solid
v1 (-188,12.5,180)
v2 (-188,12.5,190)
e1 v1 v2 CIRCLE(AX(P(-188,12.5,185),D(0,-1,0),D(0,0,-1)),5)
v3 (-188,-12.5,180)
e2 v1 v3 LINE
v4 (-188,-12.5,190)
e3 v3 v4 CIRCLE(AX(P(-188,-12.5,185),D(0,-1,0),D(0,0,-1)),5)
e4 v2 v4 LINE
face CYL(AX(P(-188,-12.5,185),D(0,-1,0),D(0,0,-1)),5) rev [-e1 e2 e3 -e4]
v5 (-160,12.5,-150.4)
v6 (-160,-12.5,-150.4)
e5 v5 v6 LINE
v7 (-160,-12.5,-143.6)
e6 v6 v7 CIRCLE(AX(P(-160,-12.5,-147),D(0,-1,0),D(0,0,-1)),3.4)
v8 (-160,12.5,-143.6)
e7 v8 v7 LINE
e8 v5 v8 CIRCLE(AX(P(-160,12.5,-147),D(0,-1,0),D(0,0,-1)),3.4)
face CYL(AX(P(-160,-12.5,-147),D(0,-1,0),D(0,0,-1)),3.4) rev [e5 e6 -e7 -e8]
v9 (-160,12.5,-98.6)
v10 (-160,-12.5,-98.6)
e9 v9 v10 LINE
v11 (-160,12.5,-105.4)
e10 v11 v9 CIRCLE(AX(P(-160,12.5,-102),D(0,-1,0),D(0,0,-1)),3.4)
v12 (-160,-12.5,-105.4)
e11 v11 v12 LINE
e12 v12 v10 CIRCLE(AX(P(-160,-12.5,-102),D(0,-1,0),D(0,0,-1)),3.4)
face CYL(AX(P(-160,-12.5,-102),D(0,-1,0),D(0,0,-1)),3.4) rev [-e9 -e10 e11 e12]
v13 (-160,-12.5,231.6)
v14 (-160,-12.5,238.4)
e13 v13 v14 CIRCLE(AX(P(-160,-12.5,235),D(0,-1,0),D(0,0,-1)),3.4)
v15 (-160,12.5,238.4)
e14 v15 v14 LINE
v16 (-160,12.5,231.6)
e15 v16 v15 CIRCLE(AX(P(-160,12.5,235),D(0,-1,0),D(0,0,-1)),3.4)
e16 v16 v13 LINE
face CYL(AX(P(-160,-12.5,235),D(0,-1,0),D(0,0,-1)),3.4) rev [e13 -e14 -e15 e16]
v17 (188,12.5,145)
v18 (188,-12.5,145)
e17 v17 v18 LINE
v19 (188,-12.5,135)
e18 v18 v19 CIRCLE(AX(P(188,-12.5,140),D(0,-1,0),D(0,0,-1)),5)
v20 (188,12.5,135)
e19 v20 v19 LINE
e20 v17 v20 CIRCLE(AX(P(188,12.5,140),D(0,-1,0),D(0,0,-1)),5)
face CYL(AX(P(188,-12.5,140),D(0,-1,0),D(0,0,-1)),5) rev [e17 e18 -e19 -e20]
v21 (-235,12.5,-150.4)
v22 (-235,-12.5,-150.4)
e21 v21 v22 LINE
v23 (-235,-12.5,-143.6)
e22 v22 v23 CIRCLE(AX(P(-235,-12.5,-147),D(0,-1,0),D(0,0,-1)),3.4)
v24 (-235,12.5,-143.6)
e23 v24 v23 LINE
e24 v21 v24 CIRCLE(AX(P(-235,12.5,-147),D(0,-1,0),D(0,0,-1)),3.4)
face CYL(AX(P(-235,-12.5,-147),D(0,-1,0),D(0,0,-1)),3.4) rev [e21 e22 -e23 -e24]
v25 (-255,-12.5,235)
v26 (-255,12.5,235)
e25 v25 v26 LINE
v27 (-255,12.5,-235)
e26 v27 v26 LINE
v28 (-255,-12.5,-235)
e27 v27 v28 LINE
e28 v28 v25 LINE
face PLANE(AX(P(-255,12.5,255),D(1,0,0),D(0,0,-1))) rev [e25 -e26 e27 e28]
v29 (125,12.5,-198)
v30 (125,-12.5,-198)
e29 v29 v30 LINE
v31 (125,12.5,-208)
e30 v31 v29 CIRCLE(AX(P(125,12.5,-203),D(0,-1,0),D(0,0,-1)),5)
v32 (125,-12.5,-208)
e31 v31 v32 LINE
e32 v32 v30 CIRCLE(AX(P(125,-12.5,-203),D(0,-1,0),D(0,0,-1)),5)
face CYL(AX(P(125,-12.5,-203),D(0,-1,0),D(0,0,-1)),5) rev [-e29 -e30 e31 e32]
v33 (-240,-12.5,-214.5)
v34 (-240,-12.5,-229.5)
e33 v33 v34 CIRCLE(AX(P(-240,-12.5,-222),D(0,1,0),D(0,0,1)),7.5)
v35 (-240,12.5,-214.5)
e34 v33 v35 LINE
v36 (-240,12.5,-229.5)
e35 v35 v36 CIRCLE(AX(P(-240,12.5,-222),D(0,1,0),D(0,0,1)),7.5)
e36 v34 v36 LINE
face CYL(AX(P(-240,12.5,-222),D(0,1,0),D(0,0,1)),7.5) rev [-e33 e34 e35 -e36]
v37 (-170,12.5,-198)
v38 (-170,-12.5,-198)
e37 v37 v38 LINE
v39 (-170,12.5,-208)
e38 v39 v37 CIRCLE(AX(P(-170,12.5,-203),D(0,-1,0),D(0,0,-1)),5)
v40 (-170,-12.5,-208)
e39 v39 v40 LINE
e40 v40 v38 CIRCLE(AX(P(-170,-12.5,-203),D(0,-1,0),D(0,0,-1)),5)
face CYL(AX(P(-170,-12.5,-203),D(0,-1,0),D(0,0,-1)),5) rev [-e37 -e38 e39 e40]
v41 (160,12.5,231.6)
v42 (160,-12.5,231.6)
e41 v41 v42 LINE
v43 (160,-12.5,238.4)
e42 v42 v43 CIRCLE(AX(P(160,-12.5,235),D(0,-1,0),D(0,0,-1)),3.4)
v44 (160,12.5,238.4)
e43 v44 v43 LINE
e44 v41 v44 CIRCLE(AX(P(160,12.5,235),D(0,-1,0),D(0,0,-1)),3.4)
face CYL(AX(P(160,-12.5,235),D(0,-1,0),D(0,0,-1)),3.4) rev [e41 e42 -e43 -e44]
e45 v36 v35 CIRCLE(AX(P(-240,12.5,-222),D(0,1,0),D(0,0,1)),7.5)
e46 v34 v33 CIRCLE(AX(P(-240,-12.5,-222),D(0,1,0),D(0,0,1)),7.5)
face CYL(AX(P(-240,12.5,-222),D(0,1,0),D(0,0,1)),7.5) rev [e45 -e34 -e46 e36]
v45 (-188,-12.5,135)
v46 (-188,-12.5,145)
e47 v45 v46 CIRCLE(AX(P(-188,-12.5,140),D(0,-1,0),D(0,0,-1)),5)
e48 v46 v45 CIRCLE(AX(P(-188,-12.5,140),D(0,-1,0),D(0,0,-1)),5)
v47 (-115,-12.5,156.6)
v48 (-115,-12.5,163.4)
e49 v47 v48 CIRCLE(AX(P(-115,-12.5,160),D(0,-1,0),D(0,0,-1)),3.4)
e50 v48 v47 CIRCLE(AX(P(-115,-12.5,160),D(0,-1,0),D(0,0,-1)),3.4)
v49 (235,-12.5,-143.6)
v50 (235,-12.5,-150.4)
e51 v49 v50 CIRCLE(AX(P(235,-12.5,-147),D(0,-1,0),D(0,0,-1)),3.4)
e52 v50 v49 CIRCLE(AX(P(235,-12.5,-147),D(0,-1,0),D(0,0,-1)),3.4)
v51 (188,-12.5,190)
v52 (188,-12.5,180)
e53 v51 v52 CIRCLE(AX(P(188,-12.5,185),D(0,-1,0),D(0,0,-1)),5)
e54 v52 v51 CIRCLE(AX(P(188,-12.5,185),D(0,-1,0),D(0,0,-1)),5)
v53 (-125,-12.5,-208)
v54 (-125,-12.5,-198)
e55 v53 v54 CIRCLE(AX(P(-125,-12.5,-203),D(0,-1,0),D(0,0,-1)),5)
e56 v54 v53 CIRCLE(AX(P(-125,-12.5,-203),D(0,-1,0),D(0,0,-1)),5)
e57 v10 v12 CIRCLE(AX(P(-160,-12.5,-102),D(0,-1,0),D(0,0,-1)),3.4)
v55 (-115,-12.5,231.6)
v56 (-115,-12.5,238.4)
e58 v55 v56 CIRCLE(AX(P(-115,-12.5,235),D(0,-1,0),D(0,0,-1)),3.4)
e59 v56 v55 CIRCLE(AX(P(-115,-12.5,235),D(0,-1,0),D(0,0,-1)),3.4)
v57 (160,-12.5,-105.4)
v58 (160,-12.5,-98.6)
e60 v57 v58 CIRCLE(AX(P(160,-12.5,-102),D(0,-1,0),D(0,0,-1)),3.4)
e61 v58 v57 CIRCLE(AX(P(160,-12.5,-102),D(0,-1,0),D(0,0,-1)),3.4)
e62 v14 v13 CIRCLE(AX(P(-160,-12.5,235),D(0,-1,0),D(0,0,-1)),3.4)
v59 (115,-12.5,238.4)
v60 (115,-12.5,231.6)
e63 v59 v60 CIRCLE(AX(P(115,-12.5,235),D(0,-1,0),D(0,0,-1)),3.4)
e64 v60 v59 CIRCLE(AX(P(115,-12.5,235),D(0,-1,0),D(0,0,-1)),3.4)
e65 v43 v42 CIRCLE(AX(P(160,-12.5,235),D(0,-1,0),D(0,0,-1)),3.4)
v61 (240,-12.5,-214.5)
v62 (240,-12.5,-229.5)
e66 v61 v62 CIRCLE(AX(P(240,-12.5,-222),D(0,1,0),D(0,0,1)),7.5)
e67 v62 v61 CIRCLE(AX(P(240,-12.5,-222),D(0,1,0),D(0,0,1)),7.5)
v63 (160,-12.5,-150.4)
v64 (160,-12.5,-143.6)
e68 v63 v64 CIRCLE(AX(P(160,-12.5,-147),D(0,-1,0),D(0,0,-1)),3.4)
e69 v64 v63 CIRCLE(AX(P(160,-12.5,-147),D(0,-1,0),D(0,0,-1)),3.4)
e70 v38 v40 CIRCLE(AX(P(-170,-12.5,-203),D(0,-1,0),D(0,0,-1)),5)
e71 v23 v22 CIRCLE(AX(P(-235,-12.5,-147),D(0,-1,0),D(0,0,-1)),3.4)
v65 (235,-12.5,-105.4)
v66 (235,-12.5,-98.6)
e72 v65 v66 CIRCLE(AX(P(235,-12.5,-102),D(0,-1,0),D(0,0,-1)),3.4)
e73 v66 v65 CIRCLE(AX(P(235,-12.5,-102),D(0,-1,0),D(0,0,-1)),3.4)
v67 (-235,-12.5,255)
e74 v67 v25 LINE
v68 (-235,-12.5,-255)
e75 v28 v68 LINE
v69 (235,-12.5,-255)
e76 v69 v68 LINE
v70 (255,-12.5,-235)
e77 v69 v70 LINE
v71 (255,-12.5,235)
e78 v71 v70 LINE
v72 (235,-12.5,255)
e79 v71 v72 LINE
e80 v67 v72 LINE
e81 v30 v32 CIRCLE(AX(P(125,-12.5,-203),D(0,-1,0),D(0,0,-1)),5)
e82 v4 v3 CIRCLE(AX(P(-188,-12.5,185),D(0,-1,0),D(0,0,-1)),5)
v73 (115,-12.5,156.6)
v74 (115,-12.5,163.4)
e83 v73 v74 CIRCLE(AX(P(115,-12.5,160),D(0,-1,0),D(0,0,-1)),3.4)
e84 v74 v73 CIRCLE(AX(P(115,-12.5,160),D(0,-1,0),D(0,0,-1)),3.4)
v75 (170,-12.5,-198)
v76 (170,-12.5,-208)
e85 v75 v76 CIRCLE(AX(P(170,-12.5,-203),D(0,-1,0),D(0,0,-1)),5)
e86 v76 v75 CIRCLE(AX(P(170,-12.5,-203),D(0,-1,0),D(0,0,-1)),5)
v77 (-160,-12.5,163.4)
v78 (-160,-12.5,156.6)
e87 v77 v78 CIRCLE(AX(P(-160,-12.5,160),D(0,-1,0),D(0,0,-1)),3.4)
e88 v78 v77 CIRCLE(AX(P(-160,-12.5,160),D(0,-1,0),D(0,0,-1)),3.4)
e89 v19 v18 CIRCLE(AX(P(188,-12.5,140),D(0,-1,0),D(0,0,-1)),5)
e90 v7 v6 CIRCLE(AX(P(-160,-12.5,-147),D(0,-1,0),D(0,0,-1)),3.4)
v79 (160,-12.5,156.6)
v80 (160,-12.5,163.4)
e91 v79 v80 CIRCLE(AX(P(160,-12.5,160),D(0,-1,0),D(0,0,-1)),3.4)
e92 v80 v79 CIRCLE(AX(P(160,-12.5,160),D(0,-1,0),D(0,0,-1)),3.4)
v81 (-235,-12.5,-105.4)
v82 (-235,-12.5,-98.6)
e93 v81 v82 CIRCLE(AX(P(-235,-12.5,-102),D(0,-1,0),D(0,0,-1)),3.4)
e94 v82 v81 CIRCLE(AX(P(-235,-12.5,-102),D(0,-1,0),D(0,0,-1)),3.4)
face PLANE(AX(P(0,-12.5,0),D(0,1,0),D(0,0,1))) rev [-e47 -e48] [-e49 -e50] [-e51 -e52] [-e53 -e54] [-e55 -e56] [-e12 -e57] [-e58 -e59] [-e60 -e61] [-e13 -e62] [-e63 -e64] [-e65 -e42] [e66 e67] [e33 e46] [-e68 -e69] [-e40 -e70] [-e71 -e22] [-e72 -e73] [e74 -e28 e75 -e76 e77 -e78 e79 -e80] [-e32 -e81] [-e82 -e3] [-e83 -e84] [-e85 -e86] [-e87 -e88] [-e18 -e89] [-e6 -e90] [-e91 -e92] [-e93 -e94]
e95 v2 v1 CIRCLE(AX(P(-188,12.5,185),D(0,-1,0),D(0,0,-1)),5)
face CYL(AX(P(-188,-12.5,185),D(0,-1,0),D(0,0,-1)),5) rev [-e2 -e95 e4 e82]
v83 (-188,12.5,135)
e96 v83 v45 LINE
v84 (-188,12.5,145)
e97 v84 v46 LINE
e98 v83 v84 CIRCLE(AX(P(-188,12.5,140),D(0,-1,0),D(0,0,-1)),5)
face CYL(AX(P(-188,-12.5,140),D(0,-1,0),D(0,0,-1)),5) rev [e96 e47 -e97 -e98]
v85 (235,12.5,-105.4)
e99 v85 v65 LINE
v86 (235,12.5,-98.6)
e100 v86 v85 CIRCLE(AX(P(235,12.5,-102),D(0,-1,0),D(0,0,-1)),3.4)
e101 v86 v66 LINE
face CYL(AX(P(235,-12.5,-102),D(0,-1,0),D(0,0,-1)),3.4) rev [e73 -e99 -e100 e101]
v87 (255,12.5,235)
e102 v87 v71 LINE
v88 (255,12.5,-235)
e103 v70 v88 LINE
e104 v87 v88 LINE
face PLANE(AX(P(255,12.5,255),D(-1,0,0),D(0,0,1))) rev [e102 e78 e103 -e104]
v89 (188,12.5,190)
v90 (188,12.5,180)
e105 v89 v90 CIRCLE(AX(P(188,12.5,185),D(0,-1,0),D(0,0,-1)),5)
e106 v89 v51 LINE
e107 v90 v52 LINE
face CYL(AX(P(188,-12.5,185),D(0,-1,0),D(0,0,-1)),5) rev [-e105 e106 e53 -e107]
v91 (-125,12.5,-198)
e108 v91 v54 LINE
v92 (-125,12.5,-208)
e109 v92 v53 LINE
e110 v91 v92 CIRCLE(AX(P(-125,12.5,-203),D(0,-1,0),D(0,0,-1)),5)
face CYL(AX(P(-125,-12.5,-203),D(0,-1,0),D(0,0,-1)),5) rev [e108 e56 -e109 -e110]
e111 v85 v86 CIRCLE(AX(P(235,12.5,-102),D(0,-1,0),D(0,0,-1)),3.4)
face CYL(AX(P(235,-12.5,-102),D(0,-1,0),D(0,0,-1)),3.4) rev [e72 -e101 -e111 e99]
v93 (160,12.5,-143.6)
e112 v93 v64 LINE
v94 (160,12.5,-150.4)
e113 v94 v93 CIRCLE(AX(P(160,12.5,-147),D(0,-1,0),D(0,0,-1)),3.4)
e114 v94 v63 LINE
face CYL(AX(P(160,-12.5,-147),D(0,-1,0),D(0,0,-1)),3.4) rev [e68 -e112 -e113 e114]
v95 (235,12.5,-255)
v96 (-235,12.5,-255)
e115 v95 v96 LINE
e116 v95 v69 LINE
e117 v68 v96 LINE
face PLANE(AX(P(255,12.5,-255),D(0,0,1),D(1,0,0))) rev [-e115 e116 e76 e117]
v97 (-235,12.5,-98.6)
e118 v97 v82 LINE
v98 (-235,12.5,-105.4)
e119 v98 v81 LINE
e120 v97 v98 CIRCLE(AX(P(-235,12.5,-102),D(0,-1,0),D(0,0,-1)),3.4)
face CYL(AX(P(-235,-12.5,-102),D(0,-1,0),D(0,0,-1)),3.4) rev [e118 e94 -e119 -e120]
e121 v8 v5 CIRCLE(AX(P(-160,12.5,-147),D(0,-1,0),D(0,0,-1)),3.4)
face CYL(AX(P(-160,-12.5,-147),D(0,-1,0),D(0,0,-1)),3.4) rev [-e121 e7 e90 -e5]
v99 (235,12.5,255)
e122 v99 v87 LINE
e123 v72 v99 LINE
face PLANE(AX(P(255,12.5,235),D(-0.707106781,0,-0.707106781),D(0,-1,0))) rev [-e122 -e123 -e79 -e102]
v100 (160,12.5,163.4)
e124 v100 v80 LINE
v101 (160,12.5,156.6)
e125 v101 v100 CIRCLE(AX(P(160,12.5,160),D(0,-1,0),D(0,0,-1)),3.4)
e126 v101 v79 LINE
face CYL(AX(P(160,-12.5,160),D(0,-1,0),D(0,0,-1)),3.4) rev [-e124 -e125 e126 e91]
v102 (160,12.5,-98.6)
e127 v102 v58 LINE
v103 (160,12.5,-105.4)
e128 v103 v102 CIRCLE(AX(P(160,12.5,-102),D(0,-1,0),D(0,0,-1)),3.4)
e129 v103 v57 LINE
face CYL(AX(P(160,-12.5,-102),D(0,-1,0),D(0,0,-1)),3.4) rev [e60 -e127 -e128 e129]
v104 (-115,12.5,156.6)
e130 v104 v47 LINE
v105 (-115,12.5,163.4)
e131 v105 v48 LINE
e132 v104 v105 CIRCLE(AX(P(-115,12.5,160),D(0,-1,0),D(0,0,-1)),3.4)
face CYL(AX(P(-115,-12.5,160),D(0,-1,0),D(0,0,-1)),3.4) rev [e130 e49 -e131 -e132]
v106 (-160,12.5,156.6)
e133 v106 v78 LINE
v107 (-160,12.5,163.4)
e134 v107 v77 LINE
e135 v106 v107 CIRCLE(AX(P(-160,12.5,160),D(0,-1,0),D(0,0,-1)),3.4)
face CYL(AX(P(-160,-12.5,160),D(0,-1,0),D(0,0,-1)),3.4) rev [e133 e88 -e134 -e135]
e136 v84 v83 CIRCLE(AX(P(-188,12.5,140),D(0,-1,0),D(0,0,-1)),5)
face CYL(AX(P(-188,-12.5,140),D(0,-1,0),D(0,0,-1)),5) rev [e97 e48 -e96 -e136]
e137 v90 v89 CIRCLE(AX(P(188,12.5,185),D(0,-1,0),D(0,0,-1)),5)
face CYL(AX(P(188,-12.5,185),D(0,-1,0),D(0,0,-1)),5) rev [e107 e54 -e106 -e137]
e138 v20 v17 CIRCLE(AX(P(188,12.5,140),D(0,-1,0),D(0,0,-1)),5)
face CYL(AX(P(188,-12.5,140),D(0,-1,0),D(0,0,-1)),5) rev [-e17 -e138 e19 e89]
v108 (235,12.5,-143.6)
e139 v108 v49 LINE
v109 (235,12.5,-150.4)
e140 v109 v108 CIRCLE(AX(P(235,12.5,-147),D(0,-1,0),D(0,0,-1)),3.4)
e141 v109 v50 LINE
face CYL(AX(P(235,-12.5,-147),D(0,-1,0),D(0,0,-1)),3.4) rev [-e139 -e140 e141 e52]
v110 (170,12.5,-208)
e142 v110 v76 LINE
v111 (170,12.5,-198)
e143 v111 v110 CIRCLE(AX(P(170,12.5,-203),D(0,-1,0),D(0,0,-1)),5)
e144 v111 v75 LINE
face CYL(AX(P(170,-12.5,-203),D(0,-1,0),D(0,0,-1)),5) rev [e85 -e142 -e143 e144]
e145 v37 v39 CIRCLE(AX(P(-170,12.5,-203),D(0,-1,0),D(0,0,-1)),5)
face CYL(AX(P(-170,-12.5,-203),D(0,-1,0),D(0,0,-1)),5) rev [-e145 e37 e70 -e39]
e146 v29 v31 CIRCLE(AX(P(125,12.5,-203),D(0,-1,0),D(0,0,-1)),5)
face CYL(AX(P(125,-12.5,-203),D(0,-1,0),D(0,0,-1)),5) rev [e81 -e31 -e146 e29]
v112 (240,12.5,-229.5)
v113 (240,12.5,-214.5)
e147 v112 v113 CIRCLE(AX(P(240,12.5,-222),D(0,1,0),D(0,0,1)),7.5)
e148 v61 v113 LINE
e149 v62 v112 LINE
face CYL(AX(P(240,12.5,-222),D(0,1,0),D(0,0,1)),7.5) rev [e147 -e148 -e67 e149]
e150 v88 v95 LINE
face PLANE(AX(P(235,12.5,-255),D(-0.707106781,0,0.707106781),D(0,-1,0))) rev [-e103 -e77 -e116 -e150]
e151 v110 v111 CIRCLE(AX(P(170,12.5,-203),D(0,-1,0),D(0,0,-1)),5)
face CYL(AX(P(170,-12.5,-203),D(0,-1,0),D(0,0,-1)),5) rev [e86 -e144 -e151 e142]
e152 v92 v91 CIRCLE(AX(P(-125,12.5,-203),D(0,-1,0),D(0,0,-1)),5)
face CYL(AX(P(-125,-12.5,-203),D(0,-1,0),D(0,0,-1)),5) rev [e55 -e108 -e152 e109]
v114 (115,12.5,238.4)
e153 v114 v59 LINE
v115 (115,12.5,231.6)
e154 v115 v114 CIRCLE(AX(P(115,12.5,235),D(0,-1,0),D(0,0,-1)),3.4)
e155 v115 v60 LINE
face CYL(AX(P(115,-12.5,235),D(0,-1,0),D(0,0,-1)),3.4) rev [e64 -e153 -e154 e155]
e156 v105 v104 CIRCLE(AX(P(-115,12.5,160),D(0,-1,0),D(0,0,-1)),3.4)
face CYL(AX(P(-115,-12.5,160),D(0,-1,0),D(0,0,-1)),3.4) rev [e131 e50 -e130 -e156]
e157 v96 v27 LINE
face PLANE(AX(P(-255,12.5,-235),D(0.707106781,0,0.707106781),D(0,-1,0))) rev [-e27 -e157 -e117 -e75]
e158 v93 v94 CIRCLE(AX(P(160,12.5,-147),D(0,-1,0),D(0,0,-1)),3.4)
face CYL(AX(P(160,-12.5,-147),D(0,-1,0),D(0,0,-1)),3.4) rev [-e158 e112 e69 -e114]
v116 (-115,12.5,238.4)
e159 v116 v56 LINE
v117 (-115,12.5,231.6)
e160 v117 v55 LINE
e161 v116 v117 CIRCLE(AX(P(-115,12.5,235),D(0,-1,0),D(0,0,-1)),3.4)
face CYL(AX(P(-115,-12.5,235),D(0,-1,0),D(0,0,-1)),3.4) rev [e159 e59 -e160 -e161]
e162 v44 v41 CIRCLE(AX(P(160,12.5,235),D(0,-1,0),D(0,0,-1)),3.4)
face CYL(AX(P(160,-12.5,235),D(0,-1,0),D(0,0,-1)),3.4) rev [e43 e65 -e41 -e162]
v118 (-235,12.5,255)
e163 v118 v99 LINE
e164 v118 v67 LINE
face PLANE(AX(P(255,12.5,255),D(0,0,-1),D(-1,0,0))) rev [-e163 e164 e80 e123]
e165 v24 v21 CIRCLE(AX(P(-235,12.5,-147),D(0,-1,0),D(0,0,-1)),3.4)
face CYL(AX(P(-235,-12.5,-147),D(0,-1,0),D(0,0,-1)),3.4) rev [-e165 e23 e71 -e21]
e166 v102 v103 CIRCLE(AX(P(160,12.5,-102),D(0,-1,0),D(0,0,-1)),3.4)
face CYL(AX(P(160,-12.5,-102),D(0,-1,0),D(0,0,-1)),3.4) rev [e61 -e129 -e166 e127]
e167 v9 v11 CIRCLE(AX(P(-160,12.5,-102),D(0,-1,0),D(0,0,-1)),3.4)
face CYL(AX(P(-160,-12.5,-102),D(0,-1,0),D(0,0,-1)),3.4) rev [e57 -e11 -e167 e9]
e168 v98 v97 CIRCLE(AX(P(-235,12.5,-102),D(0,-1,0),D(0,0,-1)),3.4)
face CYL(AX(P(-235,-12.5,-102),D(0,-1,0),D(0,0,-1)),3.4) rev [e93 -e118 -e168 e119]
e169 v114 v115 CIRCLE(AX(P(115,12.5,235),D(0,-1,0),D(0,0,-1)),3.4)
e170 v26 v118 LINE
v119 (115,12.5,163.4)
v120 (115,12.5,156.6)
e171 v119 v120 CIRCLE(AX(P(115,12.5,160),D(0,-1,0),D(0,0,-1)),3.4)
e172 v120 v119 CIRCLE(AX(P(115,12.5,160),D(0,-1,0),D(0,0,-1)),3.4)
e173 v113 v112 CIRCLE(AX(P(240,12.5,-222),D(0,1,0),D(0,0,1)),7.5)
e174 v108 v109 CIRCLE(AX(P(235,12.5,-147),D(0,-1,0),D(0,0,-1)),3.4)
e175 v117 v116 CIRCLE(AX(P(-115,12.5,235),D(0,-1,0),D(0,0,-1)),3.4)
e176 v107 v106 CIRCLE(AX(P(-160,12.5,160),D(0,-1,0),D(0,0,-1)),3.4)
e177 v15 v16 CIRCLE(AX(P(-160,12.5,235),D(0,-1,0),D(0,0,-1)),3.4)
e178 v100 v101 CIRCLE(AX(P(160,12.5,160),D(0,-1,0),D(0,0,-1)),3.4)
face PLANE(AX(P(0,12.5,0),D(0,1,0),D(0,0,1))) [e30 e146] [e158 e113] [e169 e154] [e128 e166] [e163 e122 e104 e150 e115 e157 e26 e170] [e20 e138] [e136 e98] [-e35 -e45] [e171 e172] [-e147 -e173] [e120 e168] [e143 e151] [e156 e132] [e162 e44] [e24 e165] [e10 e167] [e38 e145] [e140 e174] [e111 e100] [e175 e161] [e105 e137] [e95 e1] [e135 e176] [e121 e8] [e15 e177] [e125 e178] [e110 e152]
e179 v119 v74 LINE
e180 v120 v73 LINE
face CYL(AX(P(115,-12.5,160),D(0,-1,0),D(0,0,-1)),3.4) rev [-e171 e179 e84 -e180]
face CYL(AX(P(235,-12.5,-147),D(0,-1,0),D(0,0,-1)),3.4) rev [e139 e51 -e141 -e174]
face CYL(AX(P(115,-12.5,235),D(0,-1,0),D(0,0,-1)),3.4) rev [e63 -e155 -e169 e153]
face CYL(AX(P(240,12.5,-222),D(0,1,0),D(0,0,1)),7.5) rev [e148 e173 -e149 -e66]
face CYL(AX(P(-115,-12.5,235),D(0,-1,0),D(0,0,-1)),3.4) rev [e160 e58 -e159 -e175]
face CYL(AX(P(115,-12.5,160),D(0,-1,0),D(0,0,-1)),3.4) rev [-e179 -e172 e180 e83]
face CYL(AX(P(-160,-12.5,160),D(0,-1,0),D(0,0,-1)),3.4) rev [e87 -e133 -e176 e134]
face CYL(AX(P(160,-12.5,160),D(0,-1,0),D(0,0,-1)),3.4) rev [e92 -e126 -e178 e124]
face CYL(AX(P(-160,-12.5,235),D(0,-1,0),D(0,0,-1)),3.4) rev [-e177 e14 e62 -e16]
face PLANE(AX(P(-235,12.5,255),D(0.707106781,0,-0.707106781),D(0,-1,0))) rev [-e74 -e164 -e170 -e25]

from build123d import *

# Parameters (mm, degrees)
SKETCH_1_W              = 510
SKETCH_1_H              = 510
EXTRUDE_1_DEPTH         = 12.5
HOLE_WIZARD_10_0_10_2_D = 10
HOLE_WIZARD_15_0_15_1_D = 15
HOLE_WIZARD_M8_1_D      = 6.8
CHAMFER_1_SIZE          = 20


with BuildPart() as part:
    # 草图1 → 凸台-拉伸1 (new, symmetric)
    with BuildSketch(Plane(origin=(0, 0, 0), x_dir=(1, 0, 0), z_dir=(0, 1, 0))):
        Rectangle(SKETCH_1_W, SKETCH_1_H)
    extrude(amount=EXTRUDE_1_DEPTH, both=True)

    # Ø10.0 (10) 直径孔2 (through all)
    with Locations(Plane(origin=(0, -12.5, 0), x_dir=(-1, 0, 0), z_dir=(0, -1, 0))):
        with Locations((188, -185), (188, -140), (-188, -185), (-188, -140), (170, 203), (125, 203), (-125, 203), (-170, 203)):
            Hole(HOLE_WIZARD_10_0_10_2_D / 2)

    # Ø15.0 (15) 直径孔1 (through all)
    with Locations(Plane(origin=(0, 12.5, 0), x_dir=(1, 0, 0), z_dir=(0, 1, 0))):
        with Locations((-240, -334.568738181), (-240, 222), (240, 222), (240, -307.647208852)):
            Hole(HOLE_WIZARD_15_0_15_1_D / 2)

    # M8 螺纹孔1 (through all)
    with Locations(Plane(origin=(0, -12.5, 0), x_dir=(-1, 0, 0), z_dir=(0, -1, 0))):
        with Locations((115, -160), (160, -160), (115, -235), (160, -235), (-160, -160), (-115, -160), (-115, -235), (-160, -235), (-235, 147), (-160, 147), (-160, 102), (-235, 102), (160, 147), (235, 147), (235, 102), (160, 102)):
            Hole(HOLE_WIZARD_M8_1_D / 2)

    # 倒角1
    chamfer_1_edges = [part.edges().sort_by_distance(p)[0] for p in [
        (-255, 0, -255),
        (255, 0, -255),
        (255, 0, 255),
        (-255, 0, 255),
    ]]
    chamfer(chamfer_1_edges, length=CHAMFER_1_SIZE)


solid = part.part
